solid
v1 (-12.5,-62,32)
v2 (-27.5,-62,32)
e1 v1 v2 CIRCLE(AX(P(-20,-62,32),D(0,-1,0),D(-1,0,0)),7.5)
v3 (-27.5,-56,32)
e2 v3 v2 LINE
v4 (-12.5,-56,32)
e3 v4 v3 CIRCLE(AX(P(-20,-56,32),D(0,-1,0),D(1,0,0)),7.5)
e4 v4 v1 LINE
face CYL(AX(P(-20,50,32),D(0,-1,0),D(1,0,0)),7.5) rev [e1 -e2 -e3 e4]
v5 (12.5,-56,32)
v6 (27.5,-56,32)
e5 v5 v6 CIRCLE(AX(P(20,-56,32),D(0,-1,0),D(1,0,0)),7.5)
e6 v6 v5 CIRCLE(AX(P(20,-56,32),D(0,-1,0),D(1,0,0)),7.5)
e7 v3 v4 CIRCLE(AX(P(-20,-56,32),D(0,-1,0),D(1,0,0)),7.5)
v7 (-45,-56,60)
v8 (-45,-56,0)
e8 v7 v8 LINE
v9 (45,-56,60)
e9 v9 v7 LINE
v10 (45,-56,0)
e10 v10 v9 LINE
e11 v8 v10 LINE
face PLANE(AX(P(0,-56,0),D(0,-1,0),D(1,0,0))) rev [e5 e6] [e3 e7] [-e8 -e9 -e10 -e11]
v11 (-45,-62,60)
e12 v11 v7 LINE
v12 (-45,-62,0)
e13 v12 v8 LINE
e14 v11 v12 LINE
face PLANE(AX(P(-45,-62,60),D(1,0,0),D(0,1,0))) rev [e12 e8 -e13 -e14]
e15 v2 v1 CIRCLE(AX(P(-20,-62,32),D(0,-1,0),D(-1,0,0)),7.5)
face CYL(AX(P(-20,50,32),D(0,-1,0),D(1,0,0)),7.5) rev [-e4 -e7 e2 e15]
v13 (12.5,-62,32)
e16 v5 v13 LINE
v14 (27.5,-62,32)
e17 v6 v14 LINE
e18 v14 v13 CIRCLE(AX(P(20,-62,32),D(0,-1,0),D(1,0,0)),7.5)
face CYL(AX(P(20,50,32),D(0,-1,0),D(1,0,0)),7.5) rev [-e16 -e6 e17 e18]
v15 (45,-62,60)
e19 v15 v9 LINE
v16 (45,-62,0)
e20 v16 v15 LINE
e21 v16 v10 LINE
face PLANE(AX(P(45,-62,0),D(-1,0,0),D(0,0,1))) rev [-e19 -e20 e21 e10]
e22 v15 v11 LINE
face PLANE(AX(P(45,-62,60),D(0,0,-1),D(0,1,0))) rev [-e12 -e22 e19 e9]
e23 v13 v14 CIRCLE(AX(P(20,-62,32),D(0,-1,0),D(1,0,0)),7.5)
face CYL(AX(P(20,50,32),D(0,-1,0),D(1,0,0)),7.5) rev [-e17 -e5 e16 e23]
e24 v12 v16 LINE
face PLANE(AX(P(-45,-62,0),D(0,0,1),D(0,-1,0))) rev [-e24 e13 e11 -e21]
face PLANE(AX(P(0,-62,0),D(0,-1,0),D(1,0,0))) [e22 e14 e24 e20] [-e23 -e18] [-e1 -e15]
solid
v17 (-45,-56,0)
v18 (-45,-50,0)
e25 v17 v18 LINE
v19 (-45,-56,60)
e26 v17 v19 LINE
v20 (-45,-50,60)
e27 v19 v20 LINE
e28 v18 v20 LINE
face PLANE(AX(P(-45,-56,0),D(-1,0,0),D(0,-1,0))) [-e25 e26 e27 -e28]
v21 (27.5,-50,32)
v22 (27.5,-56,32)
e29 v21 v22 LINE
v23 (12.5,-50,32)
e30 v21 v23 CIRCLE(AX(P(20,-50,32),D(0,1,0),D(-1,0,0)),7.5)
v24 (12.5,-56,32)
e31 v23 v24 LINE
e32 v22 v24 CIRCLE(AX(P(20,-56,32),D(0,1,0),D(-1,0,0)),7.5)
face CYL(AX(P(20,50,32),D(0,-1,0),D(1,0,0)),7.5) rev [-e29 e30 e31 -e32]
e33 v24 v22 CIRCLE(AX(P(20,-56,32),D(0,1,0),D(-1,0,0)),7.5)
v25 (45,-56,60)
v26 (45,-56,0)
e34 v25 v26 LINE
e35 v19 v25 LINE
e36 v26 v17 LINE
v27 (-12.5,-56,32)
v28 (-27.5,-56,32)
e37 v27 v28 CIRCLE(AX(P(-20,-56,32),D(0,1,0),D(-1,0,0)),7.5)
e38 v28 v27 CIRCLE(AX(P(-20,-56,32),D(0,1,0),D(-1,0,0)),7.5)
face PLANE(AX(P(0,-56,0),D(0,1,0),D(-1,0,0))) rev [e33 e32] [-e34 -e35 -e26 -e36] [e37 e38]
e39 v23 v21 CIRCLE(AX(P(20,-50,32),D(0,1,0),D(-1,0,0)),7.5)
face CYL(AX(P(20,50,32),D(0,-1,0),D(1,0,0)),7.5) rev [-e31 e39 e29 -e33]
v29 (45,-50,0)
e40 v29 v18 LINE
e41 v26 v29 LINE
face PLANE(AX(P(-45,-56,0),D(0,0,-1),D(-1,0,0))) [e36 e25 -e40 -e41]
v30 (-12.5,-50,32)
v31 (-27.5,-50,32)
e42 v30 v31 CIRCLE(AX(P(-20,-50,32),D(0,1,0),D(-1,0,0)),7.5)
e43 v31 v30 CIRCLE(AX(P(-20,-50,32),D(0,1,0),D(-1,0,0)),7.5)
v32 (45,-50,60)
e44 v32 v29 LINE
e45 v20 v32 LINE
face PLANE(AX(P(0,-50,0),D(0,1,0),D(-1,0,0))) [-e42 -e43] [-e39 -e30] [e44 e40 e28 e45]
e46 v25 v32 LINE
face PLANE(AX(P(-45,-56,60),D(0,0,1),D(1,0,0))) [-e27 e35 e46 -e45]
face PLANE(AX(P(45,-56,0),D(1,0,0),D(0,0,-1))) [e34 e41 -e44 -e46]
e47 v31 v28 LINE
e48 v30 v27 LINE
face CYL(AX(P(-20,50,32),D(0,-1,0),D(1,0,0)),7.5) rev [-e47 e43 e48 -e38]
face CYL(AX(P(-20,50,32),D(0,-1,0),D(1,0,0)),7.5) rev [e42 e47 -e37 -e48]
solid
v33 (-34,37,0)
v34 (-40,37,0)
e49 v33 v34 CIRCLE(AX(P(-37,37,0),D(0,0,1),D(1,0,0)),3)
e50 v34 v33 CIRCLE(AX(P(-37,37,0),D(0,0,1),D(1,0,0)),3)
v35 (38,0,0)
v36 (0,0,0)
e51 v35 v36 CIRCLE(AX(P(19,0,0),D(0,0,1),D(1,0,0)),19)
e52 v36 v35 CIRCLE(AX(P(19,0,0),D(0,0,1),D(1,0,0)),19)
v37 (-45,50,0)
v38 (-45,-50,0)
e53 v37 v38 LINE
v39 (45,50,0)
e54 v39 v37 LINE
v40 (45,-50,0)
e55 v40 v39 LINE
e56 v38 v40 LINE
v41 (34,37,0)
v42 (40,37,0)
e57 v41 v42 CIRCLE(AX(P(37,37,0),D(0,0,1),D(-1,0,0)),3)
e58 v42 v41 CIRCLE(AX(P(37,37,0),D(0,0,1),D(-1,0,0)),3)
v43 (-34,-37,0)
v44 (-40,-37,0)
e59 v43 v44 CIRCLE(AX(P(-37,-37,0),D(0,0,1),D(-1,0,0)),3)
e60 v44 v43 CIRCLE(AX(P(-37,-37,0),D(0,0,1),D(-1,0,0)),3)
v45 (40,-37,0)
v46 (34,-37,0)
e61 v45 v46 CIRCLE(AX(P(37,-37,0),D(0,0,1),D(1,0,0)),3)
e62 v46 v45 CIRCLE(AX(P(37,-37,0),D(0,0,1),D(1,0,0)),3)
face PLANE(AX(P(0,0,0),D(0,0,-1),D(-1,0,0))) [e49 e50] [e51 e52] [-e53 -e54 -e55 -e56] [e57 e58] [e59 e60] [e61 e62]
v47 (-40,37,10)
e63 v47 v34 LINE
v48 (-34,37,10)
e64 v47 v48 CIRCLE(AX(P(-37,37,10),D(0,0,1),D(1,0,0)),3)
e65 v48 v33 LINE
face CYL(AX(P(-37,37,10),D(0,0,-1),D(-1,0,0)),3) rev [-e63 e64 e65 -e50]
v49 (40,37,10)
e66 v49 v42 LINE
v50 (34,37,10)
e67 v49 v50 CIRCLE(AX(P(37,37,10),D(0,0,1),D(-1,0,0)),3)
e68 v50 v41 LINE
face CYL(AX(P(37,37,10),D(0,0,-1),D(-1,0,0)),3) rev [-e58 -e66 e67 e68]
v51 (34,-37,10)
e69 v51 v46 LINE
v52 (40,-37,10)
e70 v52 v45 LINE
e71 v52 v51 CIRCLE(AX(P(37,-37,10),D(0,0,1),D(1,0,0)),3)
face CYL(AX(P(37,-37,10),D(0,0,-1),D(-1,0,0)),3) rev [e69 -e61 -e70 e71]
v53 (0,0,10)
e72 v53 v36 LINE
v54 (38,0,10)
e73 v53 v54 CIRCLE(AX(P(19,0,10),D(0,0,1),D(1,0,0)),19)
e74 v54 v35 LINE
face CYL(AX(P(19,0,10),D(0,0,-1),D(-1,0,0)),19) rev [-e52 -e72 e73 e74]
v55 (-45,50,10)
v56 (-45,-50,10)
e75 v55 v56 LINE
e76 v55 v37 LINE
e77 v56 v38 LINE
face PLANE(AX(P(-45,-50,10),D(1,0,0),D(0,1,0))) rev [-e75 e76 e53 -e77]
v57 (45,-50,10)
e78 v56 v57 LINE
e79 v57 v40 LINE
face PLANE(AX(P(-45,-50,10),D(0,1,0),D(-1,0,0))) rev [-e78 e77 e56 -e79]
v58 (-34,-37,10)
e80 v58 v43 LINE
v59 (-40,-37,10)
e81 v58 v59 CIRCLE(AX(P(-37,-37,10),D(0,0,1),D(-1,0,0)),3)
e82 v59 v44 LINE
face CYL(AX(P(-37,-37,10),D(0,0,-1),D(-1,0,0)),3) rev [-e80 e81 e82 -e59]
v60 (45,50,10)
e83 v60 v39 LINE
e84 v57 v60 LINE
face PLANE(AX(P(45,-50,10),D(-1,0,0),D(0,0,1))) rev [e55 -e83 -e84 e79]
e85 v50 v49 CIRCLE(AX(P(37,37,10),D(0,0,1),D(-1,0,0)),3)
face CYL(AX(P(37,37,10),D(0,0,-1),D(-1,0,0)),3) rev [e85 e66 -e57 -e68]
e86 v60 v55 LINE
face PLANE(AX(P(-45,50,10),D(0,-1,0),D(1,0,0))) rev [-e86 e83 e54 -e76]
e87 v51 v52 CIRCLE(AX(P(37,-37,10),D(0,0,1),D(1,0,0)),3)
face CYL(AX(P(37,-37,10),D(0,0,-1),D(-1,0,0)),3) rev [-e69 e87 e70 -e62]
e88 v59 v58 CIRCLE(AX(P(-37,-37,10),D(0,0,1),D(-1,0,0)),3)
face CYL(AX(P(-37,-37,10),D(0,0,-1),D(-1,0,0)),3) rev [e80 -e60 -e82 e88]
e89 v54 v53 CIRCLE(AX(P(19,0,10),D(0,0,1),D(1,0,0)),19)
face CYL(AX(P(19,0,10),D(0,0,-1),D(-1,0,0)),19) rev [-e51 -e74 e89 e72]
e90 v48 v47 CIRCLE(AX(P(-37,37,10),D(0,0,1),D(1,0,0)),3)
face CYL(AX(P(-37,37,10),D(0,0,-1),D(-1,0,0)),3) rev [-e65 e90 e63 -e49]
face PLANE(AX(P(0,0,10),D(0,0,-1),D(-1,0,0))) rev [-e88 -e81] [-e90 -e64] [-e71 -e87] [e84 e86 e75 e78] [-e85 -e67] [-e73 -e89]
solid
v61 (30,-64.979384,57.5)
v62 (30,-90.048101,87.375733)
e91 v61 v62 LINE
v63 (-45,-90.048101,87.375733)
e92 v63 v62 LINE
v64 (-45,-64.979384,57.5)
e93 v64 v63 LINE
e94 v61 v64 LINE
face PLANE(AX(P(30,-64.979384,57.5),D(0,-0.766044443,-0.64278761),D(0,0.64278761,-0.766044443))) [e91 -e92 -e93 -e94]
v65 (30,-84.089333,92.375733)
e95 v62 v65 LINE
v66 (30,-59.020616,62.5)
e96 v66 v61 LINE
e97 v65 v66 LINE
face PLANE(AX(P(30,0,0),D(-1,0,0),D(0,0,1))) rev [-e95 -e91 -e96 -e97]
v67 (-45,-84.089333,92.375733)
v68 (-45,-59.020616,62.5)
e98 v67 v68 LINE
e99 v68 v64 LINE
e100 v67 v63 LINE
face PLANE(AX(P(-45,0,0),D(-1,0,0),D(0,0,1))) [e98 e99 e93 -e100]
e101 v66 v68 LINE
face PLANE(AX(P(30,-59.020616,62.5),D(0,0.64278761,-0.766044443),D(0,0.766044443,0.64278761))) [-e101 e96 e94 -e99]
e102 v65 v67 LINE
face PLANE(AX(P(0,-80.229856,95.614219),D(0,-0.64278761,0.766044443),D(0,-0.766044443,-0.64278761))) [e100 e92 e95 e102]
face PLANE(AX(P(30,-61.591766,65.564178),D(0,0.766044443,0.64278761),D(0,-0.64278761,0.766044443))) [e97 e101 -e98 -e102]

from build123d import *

# Parameters (mm, degrees)
SKETCH_1_W          = 90
SKETCH_1_H          = 100
SKETCH_1_R          = 19
SKETCH_1_R_2        = 3
EXTRUDE_1_DEPTH     = 10
SKETCH_2_W          = 90
SKETCH_2_H          = 60
EXTRUDE_2_DEPTH     = 6
SKETCH_3_W          = 90
SKETCH_3_H          = 60
EXTRUDE_3_DEPTH     = 6
SKETCH_4_R          = 7.5
CUT_EXTRUDE_1_DEPTH = 135.792433022
EXTRUDE_1_2_DEPTH   = 75
SKETCH_6_W          = 75
SKETCH_6_H          = 7.778619134
EXTRUDE_4_DEPTH     = 35


with BuildPart() as part:
    # 草图1 → Extrude 1 (new body)
    with BuildSketch(Plane.XY):
        Rectangle(SKETCH_1_W, SKETCH_1_H)
        with Locations((19, 0)):
            Circle(SKETCH_1_R, mode=Mode.SUBTRACT)
        with Locations((-37, 37)):
            Circle(SKETCH_1_R_2, mode=Mode.SUBTRACT)
        with Locations(Location((37, 37, 0), (0, 0, 180))):
            Circle(SKETCH_1_R_2, mode=Mode.SUBTRACT)
        with Locations((37, -37)):
            Circle(SKETCH_1_R_2, mode=Mode.SUBTRACT)
        with Locations(Location((-37, -37, 0), (0, 0, 180))):
            Circle(SKETCH_1_R_2, mode=Mode.SUBTRACT)
    extrude(amount=EXTRUDE_1_DEPTH)


with BuildPart() as body_2:
    # 草图2 → 凸台-拉伸2 (new body)
    with BuildSketch(Plane(origin=(0, -50, 0), x_dir=(1, 0, 0), z_dir=(0, 1, 0))):
        with Locations((0, -30)):
            Rectangle(SKETCH_2_W, SKETCH_2_H)
    extrude(amount=-EXTRUDE_2_DEPTH)


with BuildPart() as body_3:
    # 草图3 → 凸台-拉伸3 (new body)
    with BuildSketch(Plane(origin=(0, -56, 0), x_dir=(-1, 0, 0), z_dir=(0, -1, 0))):
        with Locations((0, -30)):
            Rectangle(SKETCH_3_W, SKETCH_3_H)
    extrude(amount=EXTRUDE_3_DEPTH)


with BuildPart() as cut_extrude_1_tool:
    # 草图4 → 切除-拉伸1 (new, through all)
    with BuildSketch(Plane(origin=(0, -62, 0), x_dir=(-1, 0, 0), z_dir=(0, -1, 0))):
        with Locations(Location((-20, -32, 0), (0, 0, 180))):
            Circle(SKETCH_4_R)
        with Locations(Location((20, -32, 0), (0, 0, 180))):
            Circle(SKETCH_4_R)
    extrude(amount=-CUT_EXTRUDE_1_DEPTH)


with BuildPart() as body_2_1:
    add(body_2.part)

    # 切除-拉伸1: cut by cut_extrude_1_tool
    add(cut_extrude_1_tool.part, mode=Mode.SUBTRACT)


with BuildPart() as body_3_1:
    add(body_3.part)

    # 切除-拉伸1: cut by cut_extrude_1_tool
    add(cut_extrude_1_tool.part, mode=Mode.SUBTRACT)


with BuildPart() as body_4:
    # 草图5 → Extrude 1 2 (new body)
    with BuildSketch(Plane(origin=(-45, 0, 0), x_dir=(0, 0, -1), z_dir=(1, 0, 0))):
        Polygon((-62.5, -59.020616019), (-57.5, -64.979383981), (-60.564177772, -67.55053442), (-65.564177772, -61.591766457), align=None)
    extrude(amount=EXTRUDE_1_2_DEPTH)

    # 草图6 → 凸台-拉伸4 (add)
    with BuildSketch(Plane(origin=(0, -130.316769058, 7.897053438), x_dir=(-1, 0, 0), z_dir=(0, -0.6427876096865384, 0.7660444431189789))):
        with Locations((7.5, -85.824809787)):
            Rectangle(SKETCH_6_W, SKETCH_6_H)
    extrude(amount=EXTRUDE_4_DEPTH)


solid = Compound([part.part, body_2_1.part, body_3_1.part, body_4.part])
